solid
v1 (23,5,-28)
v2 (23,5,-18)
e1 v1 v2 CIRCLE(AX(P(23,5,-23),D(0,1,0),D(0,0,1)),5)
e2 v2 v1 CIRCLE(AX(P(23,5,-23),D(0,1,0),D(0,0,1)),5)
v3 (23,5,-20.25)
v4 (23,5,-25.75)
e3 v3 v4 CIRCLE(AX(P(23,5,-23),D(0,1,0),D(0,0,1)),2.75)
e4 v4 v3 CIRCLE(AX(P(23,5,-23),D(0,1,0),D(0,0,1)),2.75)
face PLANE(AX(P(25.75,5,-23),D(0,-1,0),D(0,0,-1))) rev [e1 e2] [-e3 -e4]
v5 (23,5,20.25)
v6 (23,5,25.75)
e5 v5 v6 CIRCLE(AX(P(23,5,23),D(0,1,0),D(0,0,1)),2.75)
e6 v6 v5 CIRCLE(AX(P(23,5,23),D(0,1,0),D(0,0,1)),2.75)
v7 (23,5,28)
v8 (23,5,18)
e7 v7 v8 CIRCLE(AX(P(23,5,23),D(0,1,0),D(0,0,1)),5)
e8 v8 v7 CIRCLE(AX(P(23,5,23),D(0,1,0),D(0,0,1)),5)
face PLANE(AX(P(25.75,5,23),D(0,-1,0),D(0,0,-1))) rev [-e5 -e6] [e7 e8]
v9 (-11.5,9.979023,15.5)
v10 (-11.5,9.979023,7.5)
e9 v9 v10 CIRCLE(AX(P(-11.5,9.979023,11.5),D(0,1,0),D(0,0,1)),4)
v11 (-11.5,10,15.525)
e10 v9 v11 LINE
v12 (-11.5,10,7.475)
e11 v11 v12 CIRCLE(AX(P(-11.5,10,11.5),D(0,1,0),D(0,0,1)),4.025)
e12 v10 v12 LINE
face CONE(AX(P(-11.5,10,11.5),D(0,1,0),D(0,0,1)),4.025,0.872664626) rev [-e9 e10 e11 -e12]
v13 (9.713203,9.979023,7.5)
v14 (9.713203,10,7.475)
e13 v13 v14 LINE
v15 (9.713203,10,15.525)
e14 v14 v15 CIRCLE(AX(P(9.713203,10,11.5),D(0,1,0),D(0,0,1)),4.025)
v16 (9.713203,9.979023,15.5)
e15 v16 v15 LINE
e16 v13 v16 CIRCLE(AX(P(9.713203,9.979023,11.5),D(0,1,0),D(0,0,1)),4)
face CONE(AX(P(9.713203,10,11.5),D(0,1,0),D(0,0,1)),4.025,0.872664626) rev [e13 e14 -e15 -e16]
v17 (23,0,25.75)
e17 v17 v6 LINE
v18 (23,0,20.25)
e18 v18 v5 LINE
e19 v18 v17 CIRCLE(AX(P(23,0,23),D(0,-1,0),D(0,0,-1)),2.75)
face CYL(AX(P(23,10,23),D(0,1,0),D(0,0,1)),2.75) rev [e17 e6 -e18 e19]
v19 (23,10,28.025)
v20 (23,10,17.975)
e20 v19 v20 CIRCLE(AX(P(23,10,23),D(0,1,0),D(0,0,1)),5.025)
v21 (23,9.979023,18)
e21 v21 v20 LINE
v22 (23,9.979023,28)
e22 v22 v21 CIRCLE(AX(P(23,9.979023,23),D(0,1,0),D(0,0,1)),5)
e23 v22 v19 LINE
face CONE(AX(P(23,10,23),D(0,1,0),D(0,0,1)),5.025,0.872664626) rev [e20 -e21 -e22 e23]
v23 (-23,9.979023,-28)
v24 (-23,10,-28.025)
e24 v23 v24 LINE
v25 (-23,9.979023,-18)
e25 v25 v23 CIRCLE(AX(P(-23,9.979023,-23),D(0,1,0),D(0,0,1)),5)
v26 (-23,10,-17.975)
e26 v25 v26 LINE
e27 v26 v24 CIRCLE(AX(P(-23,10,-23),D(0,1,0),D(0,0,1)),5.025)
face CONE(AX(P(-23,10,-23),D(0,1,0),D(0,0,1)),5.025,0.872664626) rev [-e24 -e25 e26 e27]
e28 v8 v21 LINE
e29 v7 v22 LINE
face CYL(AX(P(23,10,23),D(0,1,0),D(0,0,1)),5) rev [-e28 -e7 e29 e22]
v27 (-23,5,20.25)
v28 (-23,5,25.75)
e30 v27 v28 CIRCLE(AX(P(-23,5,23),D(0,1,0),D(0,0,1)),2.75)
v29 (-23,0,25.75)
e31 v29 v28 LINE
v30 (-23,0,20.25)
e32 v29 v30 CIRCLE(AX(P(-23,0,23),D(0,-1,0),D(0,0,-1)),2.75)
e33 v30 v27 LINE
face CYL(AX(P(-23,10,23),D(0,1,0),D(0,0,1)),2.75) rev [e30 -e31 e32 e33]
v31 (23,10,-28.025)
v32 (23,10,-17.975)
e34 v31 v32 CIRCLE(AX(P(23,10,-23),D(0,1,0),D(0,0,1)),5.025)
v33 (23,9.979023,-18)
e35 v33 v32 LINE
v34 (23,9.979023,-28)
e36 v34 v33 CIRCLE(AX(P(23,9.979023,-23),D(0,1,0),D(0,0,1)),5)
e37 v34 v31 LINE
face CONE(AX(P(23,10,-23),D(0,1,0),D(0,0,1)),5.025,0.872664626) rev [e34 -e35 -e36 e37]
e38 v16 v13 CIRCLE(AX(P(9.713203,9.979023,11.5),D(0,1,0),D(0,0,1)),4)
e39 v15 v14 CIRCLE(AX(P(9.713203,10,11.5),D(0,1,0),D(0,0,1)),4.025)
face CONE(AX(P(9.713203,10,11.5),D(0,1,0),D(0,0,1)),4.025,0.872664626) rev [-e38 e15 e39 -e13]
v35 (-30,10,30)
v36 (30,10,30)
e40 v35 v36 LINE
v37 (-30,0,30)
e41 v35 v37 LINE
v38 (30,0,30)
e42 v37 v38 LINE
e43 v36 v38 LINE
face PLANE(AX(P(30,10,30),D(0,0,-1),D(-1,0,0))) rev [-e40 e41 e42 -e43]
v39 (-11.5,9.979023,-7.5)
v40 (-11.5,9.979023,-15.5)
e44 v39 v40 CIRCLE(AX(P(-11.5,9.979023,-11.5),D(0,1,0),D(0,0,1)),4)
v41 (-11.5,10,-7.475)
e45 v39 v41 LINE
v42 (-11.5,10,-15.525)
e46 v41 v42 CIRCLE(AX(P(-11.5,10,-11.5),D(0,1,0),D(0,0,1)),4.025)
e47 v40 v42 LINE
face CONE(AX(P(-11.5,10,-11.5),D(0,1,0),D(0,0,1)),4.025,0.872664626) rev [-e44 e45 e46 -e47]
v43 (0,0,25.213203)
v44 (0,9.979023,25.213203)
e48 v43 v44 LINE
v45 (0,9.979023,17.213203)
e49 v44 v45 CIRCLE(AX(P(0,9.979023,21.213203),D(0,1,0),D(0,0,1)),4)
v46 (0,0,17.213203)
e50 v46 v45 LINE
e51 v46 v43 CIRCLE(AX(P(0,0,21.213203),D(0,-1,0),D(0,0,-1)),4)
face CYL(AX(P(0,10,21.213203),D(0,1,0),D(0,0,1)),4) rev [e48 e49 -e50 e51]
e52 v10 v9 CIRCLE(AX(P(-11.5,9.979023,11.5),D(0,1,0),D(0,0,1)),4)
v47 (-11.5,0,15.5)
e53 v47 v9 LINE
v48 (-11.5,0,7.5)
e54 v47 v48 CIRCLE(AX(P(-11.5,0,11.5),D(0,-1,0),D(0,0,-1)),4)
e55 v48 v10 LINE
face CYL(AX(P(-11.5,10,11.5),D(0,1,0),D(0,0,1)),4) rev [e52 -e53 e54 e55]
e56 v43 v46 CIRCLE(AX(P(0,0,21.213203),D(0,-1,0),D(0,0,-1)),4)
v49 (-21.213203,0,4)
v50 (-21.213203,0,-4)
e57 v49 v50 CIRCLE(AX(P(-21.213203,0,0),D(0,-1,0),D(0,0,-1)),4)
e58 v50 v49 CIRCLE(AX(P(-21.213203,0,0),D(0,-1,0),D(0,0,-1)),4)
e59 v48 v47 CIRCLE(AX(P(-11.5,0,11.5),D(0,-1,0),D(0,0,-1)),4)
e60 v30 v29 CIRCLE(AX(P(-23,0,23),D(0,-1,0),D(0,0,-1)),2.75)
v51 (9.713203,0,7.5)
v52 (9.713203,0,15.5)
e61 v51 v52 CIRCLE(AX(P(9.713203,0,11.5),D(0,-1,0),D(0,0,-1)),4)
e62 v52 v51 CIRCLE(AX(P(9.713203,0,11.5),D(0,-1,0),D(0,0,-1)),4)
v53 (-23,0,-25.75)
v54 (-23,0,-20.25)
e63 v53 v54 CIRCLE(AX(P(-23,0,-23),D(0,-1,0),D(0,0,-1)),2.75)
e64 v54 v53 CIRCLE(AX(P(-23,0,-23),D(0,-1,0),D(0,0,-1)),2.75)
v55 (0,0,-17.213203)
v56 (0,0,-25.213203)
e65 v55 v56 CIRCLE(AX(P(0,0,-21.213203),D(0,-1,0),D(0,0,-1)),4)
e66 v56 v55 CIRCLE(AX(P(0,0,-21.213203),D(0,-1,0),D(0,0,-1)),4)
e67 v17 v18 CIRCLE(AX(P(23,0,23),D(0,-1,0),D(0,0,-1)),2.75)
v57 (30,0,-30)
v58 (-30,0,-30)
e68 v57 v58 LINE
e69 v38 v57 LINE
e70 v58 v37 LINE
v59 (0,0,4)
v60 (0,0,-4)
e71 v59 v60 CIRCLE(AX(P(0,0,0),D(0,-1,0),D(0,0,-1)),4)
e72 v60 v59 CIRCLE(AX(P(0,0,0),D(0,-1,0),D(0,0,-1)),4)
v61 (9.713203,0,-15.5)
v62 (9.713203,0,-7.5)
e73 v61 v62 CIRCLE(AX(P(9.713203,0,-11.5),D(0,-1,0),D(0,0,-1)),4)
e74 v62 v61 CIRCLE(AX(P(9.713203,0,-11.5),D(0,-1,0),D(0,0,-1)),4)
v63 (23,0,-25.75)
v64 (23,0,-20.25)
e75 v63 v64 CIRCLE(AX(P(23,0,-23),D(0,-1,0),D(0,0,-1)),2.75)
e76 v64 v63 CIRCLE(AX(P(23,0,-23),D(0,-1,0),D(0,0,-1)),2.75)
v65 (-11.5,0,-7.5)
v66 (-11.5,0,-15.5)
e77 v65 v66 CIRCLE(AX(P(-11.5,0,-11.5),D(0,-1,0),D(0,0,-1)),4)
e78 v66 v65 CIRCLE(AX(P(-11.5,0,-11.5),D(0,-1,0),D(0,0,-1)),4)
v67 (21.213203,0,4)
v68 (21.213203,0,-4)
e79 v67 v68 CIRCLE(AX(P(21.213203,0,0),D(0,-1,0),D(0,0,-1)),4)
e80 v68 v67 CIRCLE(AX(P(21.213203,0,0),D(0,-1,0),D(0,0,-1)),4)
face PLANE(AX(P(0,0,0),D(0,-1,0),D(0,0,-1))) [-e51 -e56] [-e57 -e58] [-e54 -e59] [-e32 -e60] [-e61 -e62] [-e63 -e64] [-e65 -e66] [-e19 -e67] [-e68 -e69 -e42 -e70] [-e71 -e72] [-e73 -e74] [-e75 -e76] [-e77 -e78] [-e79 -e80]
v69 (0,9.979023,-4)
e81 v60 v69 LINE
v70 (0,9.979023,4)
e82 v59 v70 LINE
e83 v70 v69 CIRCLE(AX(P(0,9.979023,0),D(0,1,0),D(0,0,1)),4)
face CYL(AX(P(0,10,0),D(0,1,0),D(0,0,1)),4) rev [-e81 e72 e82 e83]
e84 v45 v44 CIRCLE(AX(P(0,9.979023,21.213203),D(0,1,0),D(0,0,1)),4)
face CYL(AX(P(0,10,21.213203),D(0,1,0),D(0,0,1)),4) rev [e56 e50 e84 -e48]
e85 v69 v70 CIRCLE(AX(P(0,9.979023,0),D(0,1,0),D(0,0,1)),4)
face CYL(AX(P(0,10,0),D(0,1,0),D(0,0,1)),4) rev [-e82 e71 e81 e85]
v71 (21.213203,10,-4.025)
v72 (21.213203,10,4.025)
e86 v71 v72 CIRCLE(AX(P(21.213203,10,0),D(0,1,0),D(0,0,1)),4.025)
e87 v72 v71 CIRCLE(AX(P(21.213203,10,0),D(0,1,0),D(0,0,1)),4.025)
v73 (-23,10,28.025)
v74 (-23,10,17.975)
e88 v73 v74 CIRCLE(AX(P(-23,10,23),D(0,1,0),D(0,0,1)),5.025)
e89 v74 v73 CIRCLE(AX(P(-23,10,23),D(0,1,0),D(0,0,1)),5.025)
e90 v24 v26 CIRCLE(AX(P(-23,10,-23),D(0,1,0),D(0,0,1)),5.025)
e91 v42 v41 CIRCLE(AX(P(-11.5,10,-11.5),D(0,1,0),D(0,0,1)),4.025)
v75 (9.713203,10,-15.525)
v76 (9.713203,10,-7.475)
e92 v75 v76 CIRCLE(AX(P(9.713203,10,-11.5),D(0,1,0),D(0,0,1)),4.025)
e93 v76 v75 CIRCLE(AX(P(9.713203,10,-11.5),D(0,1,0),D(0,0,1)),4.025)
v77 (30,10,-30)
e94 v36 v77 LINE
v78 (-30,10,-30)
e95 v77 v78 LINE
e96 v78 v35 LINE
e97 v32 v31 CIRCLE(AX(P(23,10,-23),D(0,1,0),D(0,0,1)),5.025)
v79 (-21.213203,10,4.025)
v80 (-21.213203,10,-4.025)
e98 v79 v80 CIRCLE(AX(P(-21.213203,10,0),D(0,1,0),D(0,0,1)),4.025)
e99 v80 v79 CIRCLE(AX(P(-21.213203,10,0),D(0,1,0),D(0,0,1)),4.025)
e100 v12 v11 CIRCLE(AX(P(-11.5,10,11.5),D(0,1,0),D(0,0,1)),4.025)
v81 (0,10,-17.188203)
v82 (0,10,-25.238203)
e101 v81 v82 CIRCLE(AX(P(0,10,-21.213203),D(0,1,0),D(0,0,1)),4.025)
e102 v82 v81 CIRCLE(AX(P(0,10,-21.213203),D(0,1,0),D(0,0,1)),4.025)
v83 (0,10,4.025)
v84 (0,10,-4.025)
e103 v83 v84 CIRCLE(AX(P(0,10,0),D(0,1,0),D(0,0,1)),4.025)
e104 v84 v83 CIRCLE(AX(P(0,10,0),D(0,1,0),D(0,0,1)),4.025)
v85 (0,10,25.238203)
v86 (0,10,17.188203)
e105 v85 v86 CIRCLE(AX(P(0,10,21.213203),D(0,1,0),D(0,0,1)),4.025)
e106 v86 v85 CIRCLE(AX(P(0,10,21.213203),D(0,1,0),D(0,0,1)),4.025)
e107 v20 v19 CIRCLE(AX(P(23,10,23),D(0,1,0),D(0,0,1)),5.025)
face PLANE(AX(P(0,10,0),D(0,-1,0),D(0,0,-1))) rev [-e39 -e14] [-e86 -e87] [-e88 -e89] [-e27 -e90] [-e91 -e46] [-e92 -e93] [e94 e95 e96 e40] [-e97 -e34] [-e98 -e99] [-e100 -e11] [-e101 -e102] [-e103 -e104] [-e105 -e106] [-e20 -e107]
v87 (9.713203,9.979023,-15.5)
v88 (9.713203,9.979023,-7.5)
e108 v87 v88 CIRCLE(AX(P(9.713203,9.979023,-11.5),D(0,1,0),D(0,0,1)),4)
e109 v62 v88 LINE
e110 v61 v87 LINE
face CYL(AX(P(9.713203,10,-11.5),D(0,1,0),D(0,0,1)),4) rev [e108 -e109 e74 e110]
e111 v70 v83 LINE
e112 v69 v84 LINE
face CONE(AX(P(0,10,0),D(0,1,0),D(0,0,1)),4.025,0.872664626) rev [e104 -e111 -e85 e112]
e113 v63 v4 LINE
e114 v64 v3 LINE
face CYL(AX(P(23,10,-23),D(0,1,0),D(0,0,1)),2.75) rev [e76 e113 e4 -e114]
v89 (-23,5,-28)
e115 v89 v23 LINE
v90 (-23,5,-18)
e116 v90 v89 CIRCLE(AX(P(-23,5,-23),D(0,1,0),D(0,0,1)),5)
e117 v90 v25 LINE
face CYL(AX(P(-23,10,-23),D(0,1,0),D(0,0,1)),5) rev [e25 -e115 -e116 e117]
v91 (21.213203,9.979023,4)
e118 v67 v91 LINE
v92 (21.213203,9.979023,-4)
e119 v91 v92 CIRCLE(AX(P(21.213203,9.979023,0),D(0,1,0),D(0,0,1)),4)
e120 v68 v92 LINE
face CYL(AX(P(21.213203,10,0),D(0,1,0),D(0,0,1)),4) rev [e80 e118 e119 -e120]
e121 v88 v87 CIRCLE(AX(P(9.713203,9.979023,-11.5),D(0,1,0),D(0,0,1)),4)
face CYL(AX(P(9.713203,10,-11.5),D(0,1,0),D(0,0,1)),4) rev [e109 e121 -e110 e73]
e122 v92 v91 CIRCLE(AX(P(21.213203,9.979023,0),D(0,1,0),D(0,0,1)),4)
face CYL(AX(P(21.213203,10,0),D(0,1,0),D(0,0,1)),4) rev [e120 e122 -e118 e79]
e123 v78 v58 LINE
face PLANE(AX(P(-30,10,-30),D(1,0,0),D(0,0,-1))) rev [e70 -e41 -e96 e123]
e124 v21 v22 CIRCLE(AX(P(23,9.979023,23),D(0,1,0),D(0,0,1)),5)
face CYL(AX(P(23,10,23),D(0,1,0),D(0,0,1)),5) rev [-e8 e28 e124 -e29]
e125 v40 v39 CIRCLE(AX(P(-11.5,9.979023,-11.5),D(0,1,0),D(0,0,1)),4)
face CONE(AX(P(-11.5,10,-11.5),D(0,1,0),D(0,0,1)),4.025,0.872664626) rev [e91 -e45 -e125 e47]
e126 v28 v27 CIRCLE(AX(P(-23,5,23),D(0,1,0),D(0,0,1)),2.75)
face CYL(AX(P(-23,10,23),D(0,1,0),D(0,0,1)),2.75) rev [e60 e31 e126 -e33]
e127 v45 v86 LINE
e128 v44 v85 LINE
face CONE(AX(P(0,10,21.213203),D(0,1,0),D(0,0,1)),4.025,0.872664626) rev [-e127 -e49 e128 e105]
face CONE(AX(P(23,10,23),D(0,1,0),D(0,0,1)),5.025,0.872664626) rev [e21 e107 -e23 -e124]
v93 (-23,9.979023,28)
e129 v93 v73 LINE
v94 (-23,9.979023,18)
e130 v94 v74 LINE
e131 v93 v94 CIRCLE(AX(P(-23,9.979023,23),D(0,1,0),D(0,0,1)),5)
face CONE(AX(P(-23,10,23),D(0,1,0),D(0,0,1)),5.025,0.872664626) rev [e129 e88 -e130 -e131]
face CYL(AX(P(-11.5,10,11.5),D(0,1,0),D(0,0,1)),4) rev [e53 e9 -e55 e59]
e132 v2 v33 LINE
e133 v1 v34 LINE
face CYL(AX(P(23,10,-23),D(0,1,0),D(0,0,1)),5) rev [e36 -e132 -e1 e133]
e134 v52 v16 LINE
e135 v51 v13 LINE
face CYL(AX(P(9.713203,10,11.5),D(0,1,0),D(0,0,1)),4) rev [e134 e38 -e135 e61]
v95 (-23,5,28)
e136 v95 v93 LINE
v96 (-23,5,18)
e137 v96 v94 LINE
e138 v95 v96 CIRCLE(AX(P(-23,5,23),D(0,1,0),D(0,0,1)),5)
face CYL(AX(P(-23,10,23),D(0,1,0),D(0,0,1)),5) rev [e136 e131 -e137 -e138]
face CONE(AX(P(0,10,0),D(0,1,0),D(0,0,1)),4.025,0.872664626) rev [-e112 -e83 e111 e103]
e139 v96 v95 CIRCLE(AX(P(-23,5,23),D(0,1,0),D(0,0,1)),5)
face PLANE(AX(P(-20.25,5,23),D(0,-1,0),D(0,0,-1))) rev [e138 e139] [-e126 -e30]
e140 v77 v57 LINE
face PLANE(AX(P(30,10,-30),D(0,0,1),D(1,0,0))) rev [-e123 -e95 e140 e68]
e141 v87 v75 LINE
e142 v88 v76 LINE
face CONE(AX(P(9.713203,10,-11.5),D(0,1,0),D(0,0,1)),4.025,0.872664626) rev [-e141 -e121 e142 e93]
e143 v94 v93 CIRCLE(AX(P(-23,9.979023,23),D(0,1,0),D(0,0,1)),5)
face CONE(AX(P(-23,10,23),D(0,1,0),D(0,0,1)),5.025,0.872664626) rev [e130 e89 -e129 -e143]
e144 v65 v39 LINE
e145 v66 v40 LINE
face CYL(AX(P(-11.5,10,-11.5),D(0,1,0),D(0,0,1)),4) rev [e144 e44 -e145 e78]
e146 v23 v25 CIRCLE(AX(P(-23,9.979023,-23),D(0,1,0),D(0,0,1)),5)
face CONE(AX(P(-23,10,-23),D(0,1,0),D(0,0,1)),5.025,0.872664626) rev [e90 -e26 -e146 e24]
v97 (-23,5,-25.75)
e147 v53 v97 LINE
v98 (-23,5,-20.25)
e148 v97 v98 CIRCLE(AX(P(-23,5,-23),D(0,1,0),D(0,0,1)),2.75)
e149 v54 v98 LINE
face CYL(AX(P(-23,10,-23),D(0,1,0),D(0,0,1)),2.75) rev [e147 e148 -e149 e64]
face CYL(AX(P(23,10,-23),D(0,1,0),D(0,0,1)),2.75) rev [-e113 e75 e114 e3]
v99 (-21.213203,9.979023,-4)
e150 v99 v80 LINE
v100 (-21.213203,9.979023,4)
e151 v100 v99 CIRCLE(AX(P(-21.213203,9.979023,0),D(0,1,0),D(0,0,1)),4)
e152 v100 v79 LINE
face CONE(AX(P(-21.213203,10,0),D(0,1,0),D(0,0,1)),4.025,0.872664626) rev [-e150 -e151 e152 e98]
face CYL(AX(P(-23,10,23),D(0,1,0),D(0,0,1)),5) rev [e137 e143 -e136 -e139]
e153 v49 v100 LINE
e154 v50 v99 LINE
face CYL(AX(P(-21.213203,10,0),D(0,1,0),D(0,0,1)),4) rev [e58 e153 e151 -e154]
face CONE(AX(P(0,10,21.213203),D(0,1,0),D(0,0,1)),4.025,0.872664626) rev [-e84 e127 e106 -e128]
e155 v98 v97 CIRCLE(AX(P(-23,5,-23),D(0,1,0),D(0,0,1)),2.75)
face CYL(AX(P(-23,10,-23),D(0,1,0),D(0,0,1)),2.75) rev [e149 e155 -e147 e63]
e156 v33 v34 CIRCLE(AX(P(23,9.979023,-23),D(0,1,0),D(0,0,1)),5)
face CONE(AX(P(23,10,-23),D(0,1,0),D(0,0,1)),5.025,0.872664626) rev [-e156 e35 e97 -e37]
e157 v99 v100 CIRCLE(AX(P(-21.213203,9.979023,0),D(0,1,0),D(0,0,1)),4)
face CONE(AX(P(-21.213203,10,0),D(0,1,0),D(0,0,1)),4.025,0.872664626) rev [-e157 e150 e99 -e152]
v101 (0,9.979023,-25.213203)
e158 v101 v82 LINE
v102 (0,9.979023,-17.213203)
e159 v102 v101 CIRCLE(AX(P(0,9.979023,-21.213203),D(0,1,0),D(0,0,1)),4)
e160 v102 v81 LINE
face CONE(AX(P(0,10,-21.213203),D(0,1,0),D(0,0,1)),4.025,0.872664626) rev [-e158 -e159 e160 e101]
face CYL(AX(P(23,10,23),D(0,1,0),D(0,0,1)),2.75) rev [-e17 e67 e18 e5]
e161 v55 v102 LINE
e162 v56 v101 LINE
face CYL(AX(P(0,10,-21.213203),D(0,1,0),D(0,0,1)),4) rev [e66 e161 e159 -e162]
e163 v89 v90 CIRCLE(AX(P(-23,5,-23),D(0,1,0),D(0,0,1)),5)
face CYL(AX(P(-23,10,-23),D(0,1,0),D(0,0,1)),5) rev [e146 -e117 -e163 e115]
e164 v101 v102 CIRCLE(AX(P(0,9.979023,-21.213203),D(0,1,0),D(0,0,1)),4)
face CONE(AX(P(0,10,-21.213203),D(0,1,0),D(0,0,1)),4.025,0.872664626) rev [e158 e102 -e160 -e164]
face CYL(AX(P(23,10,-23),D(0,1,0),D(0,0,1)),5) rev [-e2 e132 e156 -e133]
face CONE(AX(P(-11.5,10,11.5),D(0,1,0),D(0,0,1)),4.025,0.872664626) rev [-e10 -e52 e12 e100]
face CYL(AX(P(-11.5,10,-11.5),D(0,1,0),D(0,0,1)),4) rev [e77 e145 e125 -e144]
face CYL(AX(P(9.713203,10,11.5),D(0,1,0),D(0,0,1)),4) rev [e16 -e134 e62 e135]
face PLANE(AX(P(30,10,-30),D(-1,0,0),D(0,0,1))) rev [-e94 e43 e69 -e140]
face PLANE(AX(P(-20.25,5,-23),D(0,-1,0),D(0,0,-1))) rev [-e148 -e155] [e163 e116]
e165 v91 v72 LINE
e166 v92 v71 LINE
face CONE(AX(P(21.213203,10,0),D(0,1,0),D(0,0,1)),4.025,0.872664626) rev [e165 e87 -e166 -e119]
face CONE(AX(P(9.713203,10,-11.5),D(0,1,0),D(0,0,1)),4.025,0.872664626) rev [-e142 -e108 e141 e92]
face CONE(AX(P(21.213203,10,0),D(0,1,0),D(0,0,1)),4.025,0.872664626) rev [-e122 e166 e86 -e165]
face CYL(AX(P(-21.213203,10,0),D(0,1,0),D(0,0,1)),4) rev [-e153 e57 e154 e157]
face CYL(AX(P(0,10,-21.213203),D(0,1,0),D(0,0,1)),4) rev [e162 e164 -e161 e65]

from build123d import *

# Parameters (mm, degrees)
BASE_PLATE_PROFILE_W                   = 60
BASE_PLATE_PROFILE_H                   = 60
BASE_PLATE_60X60X10_DEPTH              = 10
CORNER_COUNTERBORES_M5_SHCS_AT_2_COUNT = 2
CORNER_COUNTERBORES_M5_SHCS_AT_2_PITCH = 46
CORNER_COUNTERBORES_M5_SHCS_AT_3_COUNT = 2
CORNER_COUNTERBORES_M5_SHCS_AT_3_PITCH = 65.053823869
CORNER_COUNTERBORES_M5_SHCS_AT_4_COUNT = 2
CORNER_COUNTERBORES_M5_SHCS_AT_4_PITCH = 46
DOWEL_HOLE_GRID_8_D                    = 8
DOWEL_HOLE_GRID_8_DEPTH                = 35.596557524
DOWEL_HOLE_GRID_8_CSINK_D              = 8.05
DOWEL_HOLE_GRID_8_CSINK_ANGLE          = 100
DOWEL_HOLE_GRID_8_TIP                  = 2.403442476


with BuildPart() as part:
    # Base Plate Profile → Base Plate 60x60x10 (new body)
    with BuildSketch(Plane(origin=(0, 0, 0), x_dir=(1, 0, 0), z_dir=(0, 1, 0))):
        Rectangle(BASE_PLATE_PROFILE_W, BASE_PLATE_PROFILE_H)
    extrude(amount=BASE_PLATE_60X60X10_DEPTH)

    # Sketch3 → Corner Counterbores M5 SHCS (revolve, cut)
    with BuildSketch(Plane(origin=(-23, 10, -23), x_dir=(0, 0, 1), z_dir=(1, 0, 0))):
        Polygon((0, 0), (0, 38), (2.75, 36.347633298), (2.75, 5), (5, 5), (5, 0.020977491), (5.025, 0), align=None)
    corner_counterbores_m5_shcs = revolve(axis=Axis((-23, 16.35, -23), (0, -1, 0)), mode=Mode.SUBTRACT)

    # Corner Counterbores M5 SHCS at 2: Corner Counterbores M5 SHCS ×2
    with Locations(*[(i * CORNER_COUNTERBORES_M5_SHCS_AT_2_PITCH, 0, 0) for i in range(1, CORNER_COUNTERBORES_M5_SHCS_AT_2_COUNT)]):
        add(corner_counterbores_m5_shcs, mode=Mode.SUBTRACT)

    # Corner Counterbores M5 SHCS at 3: Corner Counterbores M5 SHCS ×2
    with Locations(*[Vector(0.7071067811865476, 0, 0.7071067811865476) * (i * CORNER_COUNTERBORES_M5_SHCS_AT_3_PITCH) for i in range(1, CORNER_COUNTERBORES_M5_SHCS_AT_3_COUNT)]):
        add(corner_counterbores_m5_shcs, mode=Mode.SUBTRACT)

    # Corner Counterbores M5 SHCS at 4: Corner Counterbores M5 SHCS ×2
    with Locations(*[(0, 0, i * CORNER_COUNTERBORES_M5_SHCS_AT_4_PITCH) for i in range(1, CORNER_COUNTERBORES_M5_SHCS_AT_4_COUNT)]):
        add(corner_counterbores_m5_shcs, mode=Mode.SUBTRACT)

    # Dowel Hole Grid Ø8
    with Locations(Plane(origin=(0, 10, 0), x_dir=(1, 0, 0), z_dir=(0, 1, 0))):
        with Locations((-21.213203436, 0), (0, 0), (21.213203436, 0), (-11.5, 11.5), (9.713203436, 11.5), (0, 21.213203436), (-11.5, -11.5), (9.713203436, -11.5), (0, -21.213203436)):
            CounterSinkHole(DOWEL_HOLE_GRID_8_D / 2, DOWEL_HOLE_GRID_8_CSINK_D / 2, depth=DOWEL_HOLE_GRID_8_DEPTH, counter_sink_angle=DOWEL_HOLE_GRID_8_CSINK_ANGLE)
            with Locations((0, 0, -(DOWEL_HOLE_GRID_8_DEPTH + DOWEL_HOLE_GRID_8_TIP / 2))):  # 118° drill point
                Cone(0, DOWEL_HOLE_GRID_8_D / 2, DOWEL_HOLE_GRID_8_TIP, mode=Mode.SUBTRACT)


solid = part.part
